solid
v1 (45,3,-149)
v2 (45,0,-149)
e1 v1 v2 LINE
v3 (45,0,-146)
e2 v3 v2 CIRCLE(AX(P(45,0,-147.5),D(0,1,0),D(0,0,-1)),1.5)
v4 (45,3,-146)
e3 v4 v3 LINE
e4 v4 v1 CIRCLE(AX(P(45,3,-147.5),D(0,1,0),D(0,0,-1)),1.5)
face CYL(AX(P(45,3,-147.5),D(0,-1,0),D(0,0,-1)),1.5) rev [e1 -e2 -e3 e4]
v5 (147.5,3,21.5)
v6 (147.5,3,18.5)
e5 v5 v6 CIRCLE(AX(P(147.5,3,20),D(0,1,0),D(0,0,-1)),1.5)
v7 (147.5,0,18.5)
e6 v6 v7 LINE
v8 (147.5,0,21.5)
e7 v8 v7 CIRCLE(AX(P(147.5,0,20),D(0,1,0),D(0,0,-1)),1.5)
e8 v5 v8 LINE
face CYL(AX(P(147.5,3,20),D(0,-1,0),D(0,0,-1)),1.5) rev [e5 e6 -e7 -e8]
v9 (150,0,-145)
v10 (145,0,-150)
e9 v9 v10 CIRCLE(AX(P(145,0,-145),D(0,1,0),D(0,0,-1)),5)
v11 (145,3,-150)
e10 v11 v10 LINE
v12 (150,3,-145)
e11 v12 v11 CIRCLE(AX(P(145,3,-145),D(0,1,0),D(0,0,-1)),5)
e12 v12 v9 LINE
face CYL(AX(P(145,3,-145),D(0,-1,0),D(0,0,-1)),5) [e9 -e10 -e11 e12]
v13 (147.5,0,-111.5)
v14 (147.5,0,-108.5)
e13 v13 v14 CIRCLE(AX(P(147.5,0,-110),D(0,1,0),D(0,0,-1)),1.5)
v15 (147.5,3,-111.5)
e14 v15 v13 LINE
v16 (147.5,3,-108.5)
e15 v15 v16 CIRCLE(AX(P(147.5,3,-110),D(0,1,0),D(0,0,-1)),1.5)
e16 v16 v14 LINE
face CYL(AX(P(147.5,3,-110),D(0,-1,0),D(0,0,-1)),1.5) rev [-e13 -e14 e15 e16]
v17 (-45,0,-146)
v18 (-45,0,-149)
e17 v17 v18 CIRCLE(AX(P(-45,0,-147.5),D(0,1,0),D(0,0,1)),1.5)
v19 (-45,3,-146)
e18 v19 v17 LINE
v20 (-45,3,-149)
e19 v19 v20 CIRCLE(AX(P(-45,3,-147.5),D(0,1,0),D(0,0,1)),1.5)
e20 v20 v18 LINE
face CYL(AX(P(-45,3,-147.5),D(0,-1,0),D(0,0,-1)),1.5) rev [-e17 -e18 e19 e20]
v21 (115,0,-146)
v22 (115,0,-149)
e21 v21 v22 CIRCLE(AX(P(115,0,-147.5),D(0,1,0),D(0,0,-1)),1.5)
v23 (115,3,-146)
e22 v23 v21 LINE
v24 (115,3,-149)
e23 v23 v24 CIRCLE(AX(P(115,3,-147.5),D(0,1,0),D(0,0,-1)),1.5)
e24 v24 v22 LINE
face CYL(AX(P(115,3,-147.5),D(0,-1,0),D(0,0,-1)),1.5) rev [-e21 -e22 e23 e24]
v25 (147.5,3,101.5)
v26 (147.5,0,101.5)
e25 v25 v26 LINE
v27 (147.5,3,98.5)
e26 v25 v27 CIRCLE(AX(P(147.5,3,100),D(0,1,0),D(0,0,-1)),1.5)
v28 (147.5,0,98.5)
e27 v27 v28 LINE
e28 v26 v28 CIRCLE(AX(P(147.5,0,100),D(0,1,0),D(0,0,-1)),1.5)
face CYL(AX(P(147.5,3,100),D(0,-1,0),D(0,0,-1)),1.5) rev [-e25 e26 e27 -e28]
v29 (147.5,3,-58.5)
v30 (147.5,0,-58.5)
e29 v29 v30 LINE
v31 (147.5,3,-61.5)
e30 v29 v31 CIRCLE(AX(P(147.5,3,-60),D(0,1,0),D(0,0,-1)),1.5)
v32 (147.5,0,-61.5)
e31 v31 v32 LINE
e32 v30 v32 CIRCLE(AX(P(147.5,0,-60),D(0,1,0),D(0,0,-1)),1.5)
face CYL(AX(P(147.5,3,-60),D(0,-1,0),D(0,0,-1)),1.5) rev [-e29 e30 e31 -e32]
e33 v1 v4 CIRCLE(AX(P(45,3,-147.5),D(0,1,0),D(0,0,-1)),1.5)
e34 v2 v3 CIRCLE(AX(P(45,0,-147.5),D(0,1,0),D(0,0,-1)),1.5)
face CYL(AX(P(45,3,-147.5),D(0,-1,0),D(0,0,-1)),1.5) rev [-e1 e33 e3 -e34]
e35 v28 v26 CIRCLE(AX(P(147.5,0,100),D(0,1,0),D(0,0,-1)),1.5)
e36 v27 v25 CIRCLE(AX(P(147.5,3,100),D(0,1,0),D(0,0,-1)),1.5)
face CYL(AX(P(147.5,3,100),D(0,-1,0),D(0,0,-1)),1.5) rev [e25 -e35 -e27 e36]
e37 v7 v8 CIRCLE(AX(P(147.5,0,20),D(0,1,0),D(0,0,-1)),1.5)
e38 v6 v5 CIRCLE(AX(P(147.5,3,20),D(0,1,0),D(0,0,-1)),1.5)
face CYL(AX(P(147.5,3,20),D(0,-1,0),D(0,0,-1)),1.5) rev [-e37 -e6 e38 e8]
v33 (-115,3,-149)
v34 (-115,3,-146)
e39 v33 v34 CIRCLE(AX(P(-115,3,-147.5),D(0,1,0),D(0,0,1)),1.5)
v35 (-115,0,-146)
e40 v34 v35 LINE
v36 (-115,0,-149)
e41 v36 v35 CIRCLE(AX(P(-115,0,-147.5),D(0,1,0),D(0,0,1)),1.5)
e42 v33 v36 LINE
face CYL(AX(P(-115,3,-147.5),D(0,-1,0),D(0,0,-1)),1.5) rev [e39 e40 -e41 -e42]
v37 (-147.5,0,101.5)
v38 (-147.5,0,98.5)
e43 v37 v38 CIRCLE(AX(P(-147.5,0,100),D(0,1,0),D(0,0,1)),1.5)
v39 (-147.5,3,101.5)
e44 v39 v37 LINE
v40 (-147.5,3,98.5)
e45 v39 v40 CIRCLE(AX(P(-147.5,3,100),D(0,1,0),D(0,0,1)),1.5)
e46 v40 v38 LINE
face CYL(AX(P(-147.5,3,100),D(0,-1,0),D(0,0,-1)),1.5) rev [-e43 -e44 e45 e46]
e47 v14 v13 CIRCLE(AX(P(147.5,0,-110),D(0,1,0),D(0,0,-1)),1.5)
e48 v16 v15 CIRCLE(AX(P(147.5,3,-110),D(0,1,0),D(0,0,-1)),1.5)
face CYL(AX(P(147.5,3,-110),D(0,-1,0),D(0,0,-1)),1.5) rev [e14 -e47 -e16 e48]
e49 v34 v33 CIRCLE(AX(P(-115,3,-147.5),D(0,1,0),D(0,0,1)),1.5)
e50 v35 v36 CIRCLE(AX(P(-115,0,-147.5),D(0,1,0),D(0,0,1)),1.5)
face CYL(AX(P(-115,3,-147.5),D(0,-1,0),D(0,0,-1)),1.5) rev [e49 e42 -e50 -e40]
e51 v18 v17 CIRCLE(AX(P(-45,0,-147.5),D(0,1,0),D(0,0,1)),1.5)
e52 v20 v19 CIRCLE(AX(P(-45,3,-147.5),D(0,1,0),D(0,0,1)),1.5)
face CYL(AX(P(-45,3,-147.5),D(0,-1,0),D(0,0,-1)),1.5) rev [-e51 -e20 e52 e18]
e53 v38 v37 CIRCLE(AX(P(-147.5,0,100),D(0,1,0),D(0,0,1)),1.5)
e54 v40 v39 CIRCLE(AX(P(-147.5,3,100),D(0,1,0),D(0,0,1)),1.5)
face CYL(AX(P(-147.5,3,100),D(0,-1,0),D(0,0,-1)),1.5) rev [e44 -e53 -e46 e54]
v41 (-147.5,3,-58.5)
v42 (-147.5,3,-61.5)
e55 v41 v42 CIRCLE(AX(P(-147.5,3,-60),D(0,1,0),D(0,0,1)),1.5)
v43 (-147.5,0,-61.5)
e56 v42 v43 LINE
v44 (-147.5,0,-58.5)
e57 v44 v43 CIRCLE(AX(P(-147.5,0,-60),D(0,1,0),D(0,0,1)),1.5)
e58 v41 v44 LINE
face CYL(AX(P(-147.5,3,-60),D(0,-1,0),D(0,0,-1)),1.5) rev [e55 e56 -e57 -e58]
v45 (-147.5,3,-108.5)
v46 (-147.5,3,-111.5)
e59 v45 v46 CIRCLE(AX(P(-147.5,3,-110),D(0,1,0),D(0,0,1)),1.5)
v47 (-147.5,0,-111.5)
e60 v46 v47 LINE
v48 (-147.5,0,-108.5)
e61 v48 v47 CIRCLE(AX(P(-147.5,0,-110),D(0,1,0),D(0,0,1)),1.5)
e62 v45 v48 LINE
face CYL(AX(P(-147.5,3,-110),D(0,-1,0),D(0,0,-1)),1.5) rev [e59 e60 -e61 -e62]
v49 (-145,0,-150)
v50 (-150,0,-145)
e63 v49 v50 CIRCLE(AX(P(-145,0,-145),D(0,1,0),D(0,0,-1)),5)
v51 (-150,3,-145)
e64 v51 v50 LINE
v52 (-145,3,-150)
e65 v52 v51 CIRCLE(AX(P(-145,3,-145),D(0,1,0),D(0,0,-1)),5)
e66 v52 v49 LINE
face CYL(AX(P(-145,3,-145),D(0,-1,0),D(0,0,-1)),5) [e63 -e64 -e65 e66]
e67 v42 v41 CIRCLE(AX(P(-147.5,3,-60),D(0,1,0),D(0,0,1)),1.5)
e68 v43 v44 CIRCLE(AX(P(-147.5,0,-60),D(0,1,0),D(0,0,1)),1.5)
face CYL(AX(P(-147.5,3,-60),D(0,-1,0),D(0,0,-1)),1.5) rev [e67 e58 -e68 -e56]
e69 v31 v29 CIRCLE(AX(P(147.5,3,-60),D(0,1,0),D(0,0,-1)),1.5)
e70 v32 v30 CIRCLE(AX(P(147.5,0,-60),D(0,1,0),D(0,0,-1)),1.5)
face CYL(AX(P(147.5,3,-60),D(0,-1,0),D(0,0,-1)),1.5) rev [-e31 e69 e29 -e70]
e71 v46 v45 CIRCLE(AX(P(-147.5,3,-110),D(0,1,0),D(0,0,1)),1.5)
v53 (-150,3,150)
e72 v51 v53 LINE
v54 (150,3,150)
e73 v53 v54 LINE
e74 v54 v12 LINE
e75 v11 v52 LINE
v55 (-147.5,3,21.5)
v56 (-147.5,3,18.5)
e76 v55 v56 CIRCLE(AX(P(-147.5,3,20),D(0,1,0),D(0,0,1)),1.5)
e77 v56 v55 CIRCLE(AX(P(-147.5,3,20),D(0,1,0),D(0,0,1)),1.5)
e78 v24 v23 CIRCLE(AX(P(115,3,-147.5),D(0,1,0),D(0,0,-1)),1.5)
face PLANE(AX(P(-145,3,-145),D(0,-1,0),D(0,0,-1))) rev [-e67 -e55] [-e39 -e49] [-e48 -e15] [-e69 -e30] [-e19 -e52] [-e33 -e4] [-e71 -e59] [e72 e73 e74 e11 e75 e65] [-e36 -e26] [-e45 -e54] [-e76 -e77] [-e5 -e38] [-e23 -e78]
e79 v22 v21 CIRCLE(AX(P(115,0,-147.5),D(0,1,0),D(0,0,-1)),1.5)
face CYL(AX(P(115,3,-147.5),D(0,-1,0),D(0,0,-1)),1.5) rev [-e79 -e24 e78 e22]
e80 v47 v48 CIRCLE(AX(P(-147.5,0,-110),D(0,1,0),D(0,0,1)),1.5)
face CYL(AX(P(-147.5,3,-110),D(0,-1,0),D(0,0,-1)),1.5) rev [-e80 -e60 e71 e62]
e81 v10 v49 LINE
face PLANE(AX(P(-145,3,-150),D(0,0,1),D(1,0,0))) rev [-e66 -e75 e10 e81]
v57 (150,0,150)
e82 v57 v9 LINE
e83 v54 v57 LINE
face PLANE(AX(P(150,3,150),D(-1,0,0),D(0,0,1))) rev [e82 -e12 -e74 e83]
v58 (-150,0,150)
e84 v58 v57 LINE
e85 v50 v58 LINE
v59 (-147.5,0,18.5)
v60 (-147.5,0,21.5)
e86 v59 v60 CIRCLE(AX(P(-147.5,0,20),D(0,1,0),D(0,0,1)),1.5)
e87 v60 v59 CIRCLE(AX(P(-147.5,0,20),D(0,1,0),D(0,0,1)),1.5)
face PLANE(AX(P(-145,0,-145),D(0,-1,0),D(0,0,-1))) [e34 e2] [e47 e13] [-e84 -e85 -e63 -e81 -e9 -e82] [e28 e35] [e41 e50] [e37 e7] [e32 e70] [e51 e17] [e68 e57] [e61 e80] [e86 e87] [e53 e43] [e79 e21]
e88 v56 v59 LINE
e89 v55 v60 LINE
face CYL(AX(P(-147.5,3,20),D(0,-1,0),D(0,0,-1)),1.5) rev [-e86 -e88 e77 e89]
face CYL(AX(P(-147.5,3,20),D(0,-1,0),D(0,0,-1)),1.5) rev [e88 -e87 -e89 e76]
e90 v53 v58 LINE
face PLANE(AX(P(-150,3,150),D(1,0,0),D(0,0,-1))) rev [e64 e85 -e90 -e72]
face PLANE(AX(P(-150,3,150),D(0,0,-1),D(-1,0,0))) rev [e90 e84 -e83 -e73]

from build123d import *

# Parameters (mm, degrees)
SKETCH1_R           = 1.5
BOSS_EXTRUDE1_DEPTH = 3


with BuildPart() as part:
    # Sketch1 → Boss-Extrude1 (new body)
    with BuildSketch(Plane(origin=(0, 0, 0), x_dir=(1, 0, 0), z_dir=(0, 1, 0))):
        with BuildLine():
            Line((-150, -150), (150, -150))
            Line((150, -150), (150, 145))
            ThreePointArc((150, 145), (148.535533906, 148.535533906), (145, 150))
            Line((145, 150), (-145, 150))
            ThreePointArc((-145, 150), (-148.535533906, 148.535533906), (-150, 145))
            Line((-150, 145), (-150, -150))
        make_face()
        with Locations(Location((-147.5, -100, 0), (0, 0, 270))):
            Circle(SKETCH1_R, mode=Mode.SUBTRACT)
        with Locations(Location((-147.5, -20, 0), (0, 0, 270))):
            Circle(SKETCH1_R, mode=Mode.SUBTRACT)
        with Locations(Location((-147.5, 60, 0), (0, 0, 270))):
            Circle(SKETCH1_R, mode=Mode.SUBTRACT)
        with Locations(Location((-147.5, 110, 0), (0, 0, 270))):
            Circle(SKETCH1_R, mode=Mode.SUBTRACT)
        with Locations(Location((-115, 147.5, 0), (0, 0, 270))):
            Circle(SKETCH1_R, mode=Mode.SUBTRACT)
        with Locations(Location((-45, 147.5, 0), (0, 0, 270))):
            Circle(SKETCH1_R, mode=Mode.SUBTRACT)
        with Locations(Location((45, 147.5, 0), (0, 0, 90))):
            Circle(SKETCH1_R, mode=Mode.SUBTRACT)
        with Locations(Location((115, 147.5, 0), (0, 0, 90))):
            Circle(SKETCH1_R, mode=Mode.SUBTRACT)
        with Locations(Location((147.5, -20, 0), (0, 0, 90))):
            Circle(SKETCH1_R, mode=Mode.SUBTRACT)
        with Locations(Location((147.5, -100, 0), (0, 0, 90))):
            Circle(SKETCH1_R, mode=Mode.SUBTRACT)
        with Locations(Location((147.5, 110, 0), (0, 0, 90))):
            Circle(SKETCH1_R, mode=Mode.SUBTRACT)
        with Locations(Location((147.5, 60, 0), (0, 0, 90))):
            Circle(SKETCH1_R, mode=Mode.SUBTRACT)
    extrude(amount=BOSS_EXTRUDE1_DEPTH)


solid = part.part
